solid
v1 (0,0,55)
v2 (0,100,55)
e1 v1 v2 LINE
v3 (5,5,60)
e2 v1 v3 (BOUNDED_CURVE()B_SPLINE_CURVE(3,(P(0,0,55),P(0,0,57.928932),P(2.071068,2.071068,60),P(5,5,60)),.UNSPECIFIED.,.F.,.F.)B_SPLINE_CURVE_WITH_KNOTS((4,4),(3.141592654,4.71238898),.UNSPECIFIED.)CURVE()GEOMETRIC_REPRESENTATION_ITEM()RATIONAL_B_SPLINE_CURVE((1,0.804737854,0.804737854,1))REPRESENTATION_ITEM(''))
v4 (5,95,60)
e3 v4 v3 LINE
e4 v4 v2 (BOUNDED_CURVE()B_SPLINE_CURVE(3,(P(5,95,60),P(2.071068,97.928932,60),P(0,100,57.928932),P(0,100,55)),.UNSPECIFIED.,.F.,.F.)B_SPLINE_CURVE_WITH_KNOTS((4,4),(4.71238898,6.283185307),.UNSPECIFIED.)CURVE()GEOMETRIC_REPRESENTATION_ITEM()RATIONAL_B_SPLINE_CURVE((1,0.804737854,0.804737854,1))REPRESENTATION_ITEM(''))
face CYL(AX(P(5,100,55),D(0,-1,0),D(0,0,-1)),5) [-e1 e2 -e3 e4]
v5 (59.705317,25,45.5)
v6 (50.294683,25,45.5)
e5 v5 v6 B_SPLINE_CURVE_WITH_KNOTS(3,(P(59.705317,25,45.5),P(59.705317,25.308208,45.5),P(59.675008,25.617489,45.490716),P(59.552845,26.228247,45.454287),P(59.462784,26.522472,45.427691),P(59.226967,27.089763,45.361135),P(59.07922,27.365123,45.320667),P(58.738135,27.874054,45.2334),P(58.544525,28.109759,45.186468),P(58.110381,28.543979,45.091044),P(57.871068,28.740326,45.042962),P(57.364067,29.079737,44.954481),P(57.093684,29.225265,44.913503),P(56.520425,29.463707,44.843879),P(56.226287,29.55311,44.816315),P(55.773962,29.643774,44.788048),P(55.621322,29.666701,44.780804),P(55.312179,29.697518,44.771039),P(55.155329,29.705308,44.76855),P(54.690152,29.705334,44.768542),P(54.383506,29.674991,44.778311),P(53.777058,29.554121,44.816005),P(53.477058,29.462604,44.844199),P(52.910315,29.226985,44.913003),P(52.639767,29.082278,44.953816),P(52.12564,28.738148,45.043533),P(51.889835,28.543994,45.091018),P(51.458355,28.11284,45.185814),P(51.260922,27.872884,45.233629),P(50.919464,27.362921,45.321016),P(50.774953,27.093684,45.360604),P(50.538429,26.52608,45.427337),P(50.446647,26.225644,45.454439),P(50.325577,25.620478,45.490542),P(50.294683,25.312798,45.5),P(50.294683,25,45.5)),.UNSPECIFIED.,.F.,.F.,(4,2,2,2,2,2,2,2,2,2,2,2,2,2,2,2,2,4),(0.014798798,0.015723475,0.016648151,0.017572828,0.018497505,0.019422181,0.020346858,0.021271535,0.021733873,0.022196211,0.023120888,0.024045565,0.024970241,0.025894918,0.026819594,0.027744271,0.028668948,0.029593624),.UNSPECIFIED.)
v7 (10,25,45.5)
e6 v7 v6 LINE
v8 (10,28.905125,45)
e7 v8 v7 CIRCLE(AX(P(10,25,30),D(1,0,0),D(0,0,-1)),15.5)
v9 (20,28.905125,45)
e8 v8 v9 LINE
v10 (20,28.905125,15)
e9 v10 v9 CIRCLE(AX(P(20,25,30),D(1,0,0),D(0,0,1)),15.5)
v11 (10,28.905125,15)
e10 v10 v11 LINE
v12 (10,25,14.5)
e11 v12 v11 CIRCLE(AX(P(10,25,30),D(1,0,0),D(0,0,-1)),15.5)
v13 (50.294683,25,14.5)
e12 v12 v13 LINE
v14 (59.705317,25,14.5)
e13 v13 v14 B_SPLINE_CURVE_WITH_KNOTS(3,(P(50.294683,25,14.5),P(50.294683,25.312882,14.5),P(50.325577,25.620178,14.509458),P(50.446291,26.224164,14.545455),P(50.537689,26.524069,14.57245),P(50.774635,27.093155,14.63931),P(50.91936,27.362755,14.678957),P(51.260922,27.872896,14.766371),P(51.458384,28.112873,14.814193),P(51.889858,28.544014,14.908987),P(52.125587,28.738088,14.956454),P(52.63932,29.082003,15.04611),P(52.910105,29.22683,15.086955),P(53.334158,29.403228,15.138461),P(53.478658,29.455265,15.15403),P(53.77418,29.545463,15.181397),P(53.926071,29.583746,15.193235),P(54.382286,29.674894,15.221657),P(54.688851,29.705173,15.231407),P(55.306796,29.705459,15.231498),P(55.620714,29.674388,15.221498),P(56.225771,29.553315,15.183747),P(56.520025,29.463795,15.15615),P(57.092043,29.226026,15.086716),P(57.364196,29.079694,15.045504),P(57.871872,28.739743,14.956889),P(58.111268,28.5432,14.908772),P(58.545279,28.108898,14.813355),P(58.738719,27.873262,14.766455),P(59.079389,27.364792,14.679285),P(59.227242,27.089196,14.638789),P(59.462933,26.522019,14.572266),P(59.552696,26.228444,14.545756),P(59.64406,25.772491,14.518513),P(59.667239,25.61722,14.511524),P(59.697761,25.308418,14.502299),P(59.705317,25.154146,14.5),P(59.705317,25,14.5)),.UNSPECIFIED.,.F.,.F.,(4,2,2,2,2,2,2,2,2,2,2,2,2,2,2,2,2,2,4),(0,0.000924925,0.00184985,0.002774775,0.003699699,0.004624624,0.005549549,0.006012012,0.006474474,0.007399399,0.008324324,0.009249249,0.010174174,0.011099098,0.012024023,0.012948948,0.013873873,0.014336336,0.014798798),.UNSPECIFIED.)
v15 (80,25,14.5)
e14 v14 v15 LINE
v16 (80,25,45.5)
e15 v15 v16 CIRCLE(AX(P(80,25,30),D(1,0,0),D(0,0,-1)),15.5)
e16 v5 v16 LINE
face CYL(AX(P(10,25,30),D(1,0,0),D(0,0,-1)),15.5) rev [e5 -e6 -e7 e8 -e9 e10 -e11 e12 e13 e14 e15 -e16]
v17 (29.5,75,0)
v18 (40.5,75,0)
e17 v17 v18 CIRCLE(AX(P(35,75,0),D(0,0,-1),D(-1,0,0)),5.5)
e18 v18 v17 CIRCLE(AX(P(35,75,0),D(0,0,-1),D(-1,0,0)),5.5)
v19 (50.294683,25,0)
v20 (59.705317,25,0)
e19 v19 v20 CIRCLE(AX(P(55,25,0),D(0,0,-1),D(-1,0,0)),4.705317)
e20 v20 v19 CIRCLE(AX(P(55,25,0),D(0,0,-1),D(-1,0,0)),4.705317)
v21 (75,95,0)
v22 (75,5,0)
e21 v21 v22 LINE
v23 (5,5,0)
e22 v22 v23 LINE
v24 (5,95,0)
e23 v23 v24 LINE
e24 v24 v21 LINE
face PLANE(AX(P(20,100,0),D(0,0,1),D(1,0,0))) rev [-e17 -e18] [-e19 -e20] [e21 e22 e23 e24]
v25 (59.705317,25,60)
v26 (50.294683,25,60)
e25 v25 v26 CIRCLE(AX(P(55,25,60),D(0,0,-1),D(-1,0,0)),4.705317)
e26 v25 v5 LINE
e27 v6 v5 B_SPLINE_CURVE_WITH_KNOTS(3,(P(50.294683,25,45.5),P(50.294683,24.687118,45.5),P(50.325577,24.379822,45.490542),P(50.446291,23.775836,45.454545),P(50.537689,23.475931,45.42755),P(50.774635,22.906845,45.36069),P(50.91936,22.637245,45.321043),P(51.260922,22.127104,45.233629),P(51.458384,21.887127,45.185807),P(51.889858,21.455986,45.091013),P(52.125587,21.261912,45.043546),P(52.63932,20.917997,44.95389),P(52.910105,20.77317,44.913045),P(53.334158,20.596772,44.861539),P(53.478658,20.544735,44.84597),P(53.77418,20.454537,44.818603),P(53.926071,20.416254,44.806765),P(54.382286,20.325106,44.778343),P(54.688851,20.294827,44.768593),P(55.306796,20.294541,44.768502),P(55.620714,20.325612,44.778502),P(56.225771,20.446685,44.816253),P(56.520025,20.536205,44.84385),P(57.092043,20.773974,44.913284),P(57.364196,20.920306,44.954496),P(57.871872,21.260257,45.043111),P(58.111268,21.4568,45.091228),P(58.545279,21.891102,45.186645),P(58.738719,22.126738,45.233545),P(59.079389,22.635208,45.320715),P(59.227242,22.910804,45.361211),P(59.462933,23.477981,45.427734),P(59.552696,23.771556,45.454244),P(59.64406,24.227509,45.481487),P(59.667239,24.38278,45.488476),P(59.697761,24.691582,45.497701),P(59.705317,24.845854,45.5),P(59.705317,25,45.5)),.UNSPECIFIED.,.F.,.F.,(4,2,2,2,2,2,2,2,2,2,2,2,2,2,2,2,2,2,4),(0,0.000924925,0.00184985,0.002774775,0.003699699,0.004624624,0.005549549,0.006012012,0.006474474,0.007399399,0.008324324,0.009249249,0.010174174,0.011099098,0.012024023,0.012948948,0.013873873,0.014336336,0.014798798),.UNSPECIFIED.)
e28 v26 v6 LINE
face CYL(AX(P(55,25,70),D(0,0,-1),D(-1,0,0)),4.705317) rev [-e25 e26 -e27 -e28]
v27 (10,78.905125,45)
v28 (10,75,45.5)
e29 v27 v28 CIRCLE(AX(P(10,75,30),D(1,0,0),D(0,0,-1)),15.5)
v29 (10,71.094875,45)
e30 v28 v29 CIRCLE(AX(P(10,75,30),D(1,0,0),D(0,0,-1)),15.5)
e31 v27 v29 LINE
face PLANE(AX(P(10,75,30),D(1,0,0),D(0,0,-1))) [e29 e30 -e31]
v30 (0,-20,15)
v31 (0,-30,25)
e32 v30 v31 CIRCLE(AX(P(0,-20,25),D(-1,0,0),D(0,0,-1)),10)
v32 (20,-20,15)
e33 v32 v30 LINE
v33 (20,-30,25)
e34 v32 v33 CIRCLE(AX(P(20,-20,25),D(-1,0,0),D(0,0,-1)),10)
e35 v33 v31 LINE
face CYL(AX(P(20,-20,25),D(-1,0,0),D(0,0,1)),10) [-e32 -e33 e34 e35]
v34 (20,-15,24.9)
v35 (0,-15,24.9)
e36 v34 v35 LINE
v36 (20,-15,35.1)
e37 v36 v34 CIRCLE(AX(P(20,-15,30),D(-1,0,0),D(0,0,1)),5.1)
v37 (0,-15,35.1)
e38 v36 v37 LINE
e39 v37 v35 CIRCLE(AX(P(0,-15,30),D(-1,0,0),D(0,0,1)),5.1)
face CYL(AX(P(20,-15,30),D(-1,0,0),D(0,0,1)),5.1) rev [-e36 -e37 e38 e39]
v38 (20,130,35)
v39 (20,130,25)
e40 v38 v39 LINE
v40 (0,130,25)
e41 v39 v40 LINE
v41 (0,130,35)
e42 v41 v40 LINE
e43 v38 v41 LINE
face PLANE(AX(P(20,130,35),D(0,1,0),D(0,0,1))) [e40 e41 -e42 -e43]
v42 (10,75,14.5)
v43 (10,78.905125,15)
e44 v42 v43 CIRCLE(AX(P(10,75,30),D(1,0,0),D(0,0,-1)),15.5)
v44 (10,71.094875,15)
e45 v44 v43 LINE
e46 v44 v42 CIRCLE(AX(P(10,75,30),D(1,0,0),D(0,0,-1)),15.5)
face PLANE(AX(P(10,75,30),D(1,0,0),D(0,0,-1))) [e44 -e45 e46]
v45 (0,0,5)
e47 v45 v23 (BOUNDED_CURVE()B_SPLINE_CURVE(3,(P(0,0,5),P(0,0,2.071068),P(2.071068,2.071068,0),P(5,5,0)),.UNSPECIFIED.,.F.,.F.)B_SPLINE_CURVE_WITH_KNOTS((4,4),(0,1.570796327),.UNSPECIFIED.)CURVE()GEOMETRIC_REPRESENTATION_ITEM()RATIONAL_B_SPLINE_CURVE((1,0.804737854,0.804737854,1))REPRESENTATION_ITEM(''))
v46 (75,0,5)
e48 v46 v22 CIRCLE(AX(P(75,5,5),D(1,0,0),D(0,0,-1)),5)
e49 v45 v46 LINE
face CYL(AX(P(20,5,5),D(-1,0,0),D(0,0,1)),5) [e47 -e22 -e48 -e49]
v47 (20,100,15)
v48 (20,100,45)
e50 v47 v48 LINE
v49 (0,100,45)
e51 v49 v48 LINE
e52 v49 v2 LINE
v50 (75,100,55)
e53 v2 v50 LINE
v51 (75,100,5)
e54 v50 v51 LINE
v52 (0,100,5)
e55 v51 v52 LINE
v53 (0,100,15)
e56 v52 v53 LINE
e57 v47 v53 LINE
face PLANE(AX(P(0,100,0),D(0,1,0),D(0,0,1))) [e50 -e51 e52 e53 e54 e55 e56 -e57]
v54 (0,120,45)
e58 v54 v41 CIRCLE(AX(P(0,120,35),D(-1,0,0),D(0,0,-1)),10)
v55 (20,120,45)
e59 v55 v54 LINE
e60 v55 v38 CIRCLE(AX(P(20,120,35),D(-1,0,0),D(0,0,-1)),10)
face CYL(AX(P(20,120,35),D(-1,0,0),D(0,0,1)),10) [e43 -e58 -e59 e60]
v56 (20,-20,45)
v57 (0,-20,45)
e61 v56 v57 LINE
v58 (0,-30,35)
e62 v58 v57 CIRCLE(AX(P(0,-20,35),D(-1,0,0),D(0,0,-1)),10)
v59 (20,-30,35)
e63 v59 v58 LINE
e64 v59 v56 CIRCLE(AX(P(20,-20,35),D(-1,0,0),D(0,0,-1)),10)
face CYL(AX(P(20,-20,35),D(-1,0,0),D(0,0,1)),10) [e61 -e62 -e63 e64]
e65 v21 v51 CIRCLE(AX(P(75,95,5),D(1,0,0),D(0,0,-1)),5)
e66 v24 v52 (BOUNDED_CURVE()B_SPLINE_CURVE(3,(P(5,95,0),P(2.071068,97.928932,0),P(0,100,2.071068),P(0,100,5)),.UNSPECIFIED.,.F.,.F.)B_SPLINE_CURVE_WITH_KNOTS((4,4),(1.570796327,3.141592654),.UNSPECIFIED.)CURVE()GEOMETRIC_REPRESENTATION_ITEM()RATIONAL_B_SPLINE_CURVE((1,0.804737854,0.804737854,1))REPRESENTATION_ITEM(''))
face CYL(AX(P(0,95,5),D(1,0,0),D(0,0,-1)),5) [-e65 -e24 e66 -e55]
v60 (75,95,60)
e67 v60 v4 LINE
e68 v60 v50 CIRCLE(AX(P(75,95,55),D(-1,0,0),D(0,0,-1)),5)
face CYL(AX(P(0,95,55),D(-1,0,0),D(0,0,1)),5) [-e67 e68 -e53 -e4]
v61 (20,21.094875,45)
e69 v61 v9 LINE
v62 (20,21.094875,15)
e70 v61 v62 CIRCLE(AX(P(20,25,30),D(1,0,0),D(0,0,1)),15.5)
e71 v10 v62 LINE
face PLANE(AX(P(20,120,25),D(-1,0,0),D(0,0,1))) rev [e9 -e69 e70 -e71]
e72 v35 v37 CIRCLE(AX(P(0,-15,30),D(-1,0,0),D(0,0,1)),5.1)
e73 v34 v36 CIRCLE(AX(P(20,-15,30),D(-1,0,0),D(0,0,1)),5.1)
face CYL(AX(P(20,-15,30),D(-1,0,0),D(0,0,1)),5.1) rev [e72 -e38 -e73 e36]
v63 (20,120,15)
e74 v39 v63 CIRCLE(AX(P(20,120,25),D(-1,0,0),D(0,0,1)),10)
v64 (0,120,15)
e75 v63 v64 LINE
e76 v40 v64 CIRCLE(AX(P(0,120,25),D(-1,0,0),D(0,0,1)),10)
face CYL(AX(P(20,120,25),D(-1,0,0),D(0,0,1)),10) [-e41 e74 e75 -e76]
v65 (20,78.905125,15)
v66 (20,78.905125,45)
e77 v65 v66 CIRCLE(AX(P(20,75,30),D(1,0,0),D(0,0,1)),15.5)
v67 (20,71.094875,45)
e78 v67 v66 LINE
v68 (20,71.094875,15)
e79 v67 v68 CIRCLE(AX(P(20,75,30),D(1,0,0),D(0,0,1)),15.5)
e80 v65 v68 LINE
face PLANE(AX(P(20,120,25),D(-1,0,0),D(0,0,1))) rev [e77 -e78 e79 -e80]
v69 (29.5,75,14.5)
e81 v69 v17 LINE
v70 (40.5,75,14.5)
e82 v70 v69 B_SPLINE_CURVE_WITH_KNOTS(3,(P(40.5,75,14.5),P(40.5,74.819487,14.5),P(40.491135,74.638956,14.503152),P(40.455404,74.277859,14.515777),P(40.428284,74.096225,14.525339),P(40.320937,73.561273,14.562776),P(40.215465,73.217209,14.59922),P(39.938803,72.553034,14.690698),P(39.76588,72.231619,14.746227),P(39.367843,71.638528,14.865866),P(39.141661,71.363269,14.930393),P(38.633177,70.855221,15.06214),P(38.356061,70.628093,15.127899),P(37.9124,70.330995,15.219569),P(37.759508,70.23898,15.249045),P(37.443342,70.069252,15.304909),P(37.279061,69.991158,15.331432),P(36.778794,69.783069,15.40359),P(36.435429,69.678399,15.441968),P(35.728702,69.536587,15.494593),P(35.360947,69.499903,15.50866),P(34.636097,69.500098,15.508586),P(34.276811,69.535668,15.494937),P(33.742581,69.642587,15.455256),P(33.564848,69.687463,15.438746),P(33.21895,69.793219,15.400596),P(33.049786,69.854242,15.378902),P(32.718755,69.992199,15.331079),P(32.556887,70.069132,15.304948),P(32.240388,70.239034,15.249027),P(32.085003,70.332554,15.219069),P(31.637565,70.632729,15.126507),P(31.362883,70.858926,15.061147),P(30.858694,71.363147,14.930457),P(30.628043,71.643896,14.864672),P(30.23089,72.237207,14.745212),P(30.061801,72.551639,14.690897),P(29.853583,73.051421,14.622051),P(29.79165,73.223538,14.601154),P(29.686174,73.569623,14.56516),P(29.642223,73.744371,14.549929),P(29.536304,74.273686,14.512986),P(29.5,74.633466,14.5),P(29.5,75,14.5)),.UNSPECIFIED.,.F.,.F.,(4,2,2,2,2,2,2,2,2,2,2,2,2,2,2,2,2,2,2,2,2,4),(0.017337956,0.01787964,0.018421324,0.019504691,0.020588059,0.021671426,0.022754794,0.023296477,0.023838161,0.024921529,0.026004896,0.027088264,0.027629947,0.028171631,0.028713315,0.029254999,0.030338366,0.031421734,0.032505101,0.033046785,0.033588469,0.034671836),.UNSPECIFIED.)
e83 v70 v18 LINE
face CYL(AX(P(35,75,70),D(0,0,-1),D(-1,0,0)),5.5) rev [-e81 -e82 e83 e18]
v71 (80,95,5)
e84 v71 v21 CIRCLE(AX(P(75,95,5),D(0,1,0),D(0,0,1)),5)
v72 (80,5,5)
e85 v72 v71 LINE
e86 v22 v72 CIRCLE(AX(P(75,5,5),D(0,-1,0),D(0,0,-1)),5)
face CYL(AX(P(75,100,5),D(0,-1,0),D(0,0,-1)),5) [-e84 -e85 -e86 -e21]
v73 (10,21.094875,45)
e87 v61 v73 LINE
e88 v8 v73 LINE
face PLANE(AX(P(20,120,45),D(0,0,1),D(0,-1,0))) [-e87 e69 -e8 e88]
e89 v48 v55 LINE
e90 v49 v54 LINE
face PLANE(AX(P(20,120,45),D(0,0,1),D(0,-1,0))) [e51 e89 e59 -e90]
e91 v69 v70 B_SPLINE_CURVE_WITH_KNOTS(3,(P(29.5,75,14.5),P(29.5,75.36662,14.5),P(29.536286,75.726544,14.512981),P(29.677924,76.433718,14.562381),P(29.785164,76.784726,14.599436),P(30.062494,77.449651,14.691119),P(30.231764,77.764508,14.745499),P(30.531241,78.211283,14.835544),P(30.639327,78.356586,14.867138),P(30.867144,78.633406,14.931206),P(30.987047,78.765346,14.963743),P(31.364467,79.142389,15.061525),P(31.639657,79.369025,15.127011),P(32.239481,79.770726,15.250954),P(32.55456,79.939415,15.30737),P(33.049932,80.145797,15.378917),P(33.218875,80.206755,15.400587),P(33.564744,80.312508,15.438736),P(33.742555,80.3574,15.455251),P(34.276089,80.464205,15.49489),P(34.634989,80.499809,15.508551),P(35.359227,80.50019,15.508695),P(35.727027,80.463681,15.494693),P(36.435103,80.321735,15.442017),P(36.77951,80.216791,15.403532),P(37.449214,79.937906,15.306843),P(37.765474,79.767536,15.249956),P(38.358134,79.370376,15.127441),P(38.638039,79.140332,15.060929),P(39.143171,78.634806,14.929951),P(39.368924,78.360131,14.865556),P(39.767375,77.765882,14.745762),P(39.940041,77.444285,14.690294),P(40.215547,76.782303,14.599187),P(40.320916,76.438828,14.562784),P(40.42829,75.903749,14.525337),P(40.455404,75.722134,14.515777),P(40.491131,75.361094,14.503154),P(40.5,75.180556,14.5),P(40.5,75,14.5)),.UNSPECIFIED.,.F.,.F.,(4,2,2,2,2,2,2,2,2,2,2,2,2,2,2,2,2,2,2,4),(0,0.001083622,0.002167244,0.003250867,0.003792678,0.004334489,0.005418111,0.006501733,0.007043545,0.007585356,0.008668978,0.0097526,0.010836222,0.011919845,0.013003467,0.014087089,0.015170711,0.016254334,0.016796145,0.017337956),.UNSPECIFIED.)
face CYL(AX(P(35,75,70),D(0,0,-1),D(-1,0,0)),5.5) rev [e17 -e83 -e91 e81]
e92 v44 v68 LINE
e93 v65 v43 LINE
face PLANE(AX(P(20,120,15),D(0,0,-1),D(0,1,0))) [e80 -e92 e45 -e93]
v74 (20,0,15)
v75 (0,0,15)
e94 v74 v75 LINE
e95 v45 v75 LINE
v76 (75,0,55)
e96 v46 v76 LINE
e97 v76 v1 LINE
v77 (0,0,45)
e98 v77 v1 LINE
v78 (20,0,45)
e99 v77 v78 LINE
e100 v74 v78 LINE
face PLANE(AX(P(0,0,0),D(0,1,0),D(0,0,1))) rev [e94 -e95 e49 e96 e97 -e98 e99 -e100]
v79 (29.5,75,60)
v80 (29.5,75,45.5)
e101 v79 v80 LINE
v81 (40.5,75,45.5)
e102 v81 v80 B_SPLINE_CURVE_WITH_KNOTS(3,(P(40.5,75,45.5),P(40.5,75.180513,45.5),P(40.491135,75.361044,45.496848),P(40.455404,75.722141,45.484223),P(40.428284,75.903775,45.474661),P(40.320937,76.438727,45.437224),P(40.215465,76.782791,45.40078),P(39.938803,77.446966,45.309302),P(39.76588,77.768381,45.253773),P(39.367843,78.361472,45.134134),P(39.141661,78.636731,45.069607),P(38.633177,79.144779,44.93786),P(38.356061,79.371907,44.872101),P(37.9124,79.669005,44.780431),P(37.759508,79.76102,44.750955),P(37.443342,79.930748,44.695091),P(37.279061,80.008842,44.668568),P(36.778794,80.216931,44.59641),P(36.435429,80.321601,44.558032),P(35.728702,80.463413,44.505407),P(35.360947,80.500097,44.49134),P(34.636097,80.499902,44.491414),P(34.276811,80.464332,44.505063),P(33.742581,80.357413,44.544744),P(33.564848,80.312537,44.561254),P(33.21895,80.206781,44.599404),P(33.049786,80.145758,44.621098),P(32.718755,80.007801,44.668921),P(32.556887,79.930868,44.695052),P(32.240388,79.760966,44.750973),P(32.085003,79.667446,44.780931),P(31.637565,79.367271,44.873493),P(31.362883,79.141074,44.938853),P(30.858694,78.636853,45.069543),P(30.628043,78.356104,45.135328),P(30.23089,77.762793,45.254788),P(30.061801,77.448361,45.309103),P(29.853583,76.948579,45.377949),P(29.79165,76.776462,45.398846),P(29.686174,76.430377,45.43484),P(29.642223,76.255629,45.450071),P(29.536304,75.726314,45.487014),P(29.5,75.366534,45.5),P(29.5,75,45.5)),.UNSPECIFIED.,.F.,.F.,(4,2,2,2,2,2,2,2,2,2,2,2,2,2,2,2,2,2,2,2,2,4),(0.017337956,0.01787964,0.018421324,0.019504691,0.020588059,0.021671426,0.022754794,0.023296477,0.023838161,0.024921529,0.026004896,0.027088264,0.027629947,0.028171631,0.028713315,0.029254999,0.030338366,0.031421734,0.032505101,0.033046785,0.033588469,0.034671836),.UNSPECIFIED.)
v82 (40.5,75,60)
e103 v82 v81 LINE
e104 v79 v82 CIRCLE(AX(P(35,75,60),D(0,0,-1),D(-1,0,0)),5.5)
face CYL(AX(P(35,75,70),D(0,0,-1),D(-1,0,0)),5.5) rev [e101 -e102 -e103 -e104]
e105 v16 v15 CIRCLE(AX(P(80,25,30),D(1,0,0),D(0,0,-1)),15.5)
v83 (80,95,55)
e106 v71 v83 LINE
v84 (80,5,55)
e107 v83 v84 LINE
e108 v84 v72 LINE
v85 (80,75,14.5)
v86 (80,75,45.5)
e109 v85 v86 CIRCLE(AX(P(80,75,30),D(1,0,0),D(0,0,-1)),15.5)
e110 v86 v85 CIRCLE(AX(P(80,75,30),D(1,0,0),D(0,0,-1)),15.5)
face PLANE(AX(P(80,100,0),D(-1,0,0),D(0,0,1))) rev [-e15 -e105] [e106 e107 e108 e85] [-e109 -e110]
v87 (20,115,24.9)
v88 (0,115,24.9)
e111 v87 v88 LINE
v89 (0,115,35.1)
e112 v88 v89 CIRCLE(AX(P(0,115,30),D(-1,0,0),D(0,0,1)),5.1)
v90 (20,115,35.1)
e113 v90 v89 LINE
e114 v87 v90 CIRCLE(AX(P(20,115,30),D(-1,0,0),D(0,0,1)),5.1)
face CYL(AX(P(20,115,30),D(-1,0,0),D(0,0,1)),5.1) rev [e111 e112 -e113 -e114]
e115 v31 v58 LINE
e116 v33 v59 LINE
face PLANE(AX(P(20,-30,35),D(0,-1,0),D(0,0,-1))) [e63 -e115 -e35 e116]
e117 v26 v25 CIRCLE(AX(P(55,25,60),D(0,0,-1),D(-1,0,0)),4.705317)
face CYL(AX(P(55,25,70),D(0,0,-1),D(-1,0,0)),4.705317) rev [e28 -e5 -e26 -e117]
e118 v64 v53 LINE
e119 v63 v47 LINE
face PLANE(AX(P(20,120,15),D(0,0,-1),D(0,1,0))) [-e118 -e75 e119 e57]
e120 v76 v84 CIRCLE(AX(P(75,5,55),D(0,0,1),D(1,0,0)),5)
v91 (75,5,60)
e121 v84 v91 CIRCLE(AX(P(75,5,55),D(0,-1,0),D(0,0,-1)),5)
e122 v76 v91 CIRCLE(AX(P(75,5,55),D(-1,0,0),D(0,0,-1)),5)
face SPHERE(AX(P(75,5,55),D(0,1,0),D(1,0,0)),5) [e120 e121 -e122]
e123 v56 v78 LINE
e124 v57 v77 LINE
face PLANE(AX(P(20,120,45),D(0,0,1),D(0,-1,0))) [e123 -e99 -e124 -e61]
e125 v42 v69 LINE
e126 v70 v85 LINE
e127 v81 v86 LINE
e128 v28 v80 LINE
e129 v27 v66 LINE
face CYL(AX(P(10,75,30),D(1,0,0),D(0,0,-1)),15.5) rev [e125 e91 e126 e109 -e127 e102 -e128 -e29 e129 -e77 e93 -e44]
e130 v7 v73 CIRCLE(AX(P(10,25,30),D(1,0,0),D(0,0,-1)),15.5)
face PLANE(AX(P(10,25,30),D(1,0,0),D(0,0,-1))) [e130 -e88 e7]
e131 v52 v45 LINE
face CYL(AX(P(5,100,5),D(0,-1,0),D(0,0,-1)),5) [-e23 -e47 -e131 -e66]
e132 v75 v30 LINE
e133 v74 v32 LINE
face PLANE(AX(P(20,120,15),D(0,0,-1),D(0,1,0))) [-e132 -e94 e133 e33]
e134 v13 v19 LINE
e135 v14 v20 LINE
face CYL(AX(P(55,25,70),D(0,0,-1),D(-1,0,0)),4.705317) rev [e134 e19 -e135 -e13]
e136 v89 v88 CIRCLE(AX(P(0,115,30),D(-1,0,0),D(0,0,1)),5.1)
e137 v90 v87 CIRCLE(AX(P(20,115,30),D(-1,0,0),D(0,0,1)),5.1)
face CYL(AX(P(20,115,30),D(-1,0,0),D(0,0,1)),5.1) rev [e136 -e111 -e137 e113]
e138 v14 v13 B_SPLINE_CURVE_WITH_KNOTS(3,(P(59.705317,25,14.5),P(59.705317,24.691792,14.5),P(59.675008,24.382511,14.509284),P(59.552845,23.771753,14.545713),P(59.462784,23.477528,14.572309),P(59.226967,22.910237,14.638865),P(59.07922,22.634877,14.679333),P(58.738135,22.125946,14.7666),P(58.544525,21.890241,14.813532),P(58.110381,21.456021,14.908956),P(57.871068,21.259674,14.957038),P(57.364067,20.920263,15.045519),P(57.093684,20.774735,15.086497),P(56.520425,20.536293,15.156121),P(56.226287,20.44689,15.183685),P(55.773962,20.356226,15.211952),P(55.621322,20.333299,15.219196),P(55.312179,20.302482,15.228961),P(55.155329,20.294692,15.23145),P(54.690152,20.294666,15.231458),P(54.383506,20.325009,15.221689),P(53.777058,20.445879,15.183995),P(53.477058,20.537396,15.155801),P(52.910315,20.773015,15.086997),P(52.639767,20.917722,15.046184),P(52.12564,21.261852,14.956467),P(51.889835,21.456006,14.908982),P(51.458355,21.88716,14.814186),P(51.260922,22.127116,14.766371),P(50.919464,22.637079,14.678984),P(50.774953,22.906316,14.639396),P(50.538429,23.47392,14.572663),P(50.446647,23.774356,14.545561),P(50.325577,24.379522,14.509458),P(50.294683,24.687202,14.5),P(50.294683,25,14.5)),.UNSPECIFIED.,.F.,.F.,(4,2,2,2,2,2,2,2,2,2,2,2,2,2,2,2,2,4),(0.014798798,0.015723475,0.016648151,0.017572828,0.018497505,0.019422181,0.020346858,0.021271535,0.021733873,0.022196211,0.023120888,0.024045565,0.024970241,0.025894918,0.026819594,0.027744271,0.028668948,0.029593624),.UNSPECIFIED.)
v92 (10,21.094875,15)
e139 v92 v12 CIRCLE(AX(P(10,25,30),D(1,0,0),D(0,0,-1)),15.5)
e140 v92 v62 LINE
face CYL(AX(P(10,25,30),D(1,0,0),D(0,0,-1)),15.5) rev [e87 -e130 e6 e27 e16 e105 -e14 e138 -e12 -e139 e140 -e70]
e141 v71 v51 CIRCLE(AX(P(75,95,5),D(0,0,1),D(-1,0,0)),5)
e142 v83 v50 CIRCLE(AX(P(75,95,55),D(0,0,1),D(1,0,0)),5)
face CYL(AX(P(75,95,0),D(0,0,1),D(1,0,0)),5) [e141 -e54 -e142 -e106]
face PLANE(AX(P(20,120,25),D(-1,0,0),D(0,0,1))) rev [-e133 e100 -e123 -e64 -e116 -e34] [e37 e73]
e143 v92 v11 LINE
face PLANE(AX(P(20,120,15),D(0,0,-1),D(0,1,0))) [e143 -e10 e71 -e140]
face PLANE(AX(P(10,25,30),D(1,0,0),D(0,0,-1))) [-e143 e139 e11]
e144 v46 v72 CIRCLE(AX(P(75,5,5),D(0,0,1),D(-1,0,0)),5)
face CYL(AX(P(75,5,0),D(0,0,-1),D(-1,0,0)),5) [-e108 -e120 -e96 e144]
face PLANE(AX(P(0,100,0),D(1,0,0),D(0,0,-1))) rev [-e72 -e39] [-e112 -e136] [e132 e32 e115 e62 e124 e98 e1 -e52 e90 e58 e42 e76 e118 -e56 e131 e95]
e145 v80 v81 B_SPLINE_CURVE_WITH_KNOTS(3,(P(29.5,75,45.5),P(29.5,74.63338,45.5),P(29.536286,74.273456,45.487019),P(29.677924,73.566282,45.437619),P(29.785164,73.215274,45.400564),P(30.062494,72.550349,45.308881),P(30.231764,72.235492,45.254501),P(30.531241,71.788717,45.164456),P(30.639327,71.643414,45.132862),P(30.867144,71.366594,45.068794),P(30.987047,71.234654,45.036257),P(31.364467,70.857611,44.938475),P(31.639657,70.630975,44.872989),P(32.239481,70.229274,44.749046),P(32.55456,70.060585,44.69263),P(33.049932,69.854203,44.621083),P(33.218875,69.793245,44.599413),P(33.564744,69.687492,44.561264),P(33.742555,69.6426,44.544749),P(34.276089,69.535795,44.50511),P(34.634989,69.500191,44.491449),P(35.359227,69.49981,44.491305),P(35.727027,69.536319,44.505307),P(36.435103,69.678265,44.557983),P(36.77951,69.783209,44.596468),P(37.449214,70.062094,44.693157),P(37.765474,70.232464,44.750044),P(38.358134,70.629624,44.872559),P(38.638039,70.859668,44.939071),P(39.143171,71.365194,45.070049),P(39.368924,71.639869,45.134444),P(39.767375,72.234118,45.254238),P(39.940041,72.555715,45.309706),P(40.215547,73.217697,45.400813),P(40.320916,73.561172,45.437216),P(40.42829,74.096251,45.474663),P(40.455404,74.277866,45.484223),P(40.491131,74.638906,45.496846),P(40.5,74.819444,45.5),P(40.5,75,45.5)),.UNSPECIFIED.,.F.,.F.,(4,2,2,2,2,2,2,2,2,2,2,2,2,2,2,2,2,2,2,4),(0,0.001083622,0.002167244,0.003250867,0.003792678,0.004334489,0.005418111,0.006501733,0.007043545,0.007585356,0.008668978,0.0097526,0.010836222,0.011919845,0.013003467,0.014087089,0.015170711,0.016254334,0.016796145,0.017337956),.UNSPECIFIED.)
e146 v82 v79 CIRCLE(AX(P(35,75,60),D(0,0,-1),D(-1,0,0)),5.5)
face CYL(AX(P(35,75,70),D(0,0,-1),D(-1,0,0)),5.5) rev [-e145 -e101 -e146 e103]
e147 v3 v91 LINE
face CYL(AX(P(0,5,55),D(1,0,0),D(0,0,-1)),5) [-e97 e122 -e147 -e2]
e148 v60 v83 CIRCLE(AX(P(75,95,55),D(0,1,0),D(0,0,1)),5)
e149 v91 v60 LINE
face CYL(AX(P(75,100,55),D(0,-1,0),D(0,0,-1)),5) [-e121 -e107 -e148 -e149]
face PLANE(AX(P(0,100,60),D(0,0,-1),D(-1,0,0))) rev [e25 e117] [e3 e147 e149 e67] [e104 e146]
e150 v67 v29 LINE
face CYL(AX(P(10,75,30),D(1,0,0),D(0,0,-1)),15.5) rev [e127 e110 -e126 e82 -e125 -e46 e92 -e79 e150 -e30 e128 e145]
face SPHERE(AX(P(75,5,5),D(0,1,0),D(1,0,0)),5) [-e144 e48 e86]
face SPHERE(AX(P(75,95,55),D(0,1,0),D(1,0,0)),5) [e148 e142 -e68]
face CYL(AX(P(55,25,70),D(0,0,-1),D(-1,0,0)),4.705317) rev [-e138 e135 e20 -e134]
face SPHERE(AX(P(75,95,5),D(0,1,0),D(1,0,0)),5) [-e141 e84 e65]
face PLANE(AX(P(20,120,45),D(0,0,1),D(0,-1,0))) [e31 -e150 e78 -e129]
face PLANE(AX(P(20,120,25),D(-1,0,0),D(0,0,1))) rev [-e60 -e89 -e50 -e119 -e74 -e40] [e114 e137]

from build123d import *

# Parameters (mm, degrees)
BOSS_EXTRUDE1_DEPTH = 100
SKETCH2_R           = 15.5
CUT_EXTRUDE1_DEPTH  = 70
SKETCH3_R           = 5.1
CUT_EXTRUDE2_DEPTH  = 70
SKETCH4_R           = 5.5
SKETCH4_R_2         = 4.705316684
CUT_EXTRUDE3_DEPTH  = 70
SKETCH5_R           = 5.1
BOSS_EXTRUDE2_DEPTH = 20
SKETCH6_W           = 20
SKETCH6_H           = 100
CUT_EXTRUDE4_DEPTH  = 20
FILLET1_R           = 5


with BuildPart() as part:
    # Sketch1 → Boss-Extrude1 (new body)
    with BuildSketch(Plane(origin=(0, 0, 0), x_dir=(1, 0, 0), z_dir=(0, 1, 0))):
        Polygon((0, 20), (20, 20), (20, 0), (80, 0), (80, -60), (0, -60), (0, 0), align=None)
    extrude(amount=BOSS_EXTRUDE1_DEPTH)

    # Sketch2 → Cut-Extrude1 (cut)
    with BuildSketch(Plane(origin=(80, 0, 0), x_dir=(0, 0, -1), z_dir=(1, 0, 0))):
        with Locations((-30, 75)):
            Circle(SKETCH2_R)
        with Locations((-30, 25)):
            Circle(SKETCH2_R)
    extrude(amount=-CUT_EXTRUDE1_DEPTH, mode=Mode.SUBTRACT)

    # Sketch3 → Cut-Extrude2 (cut)
    with BuildSketch(Plane(origin=(20, 0, 0), x_dir=(0, 0, -1), z_dir=(1, 0, 0))):
        with Locations((10, 87.5)):
            Circle(SKETCH3_R)
        with Locations((10, 12.5)):
            Circle(SKETCH3_R)
        with Locations((10, 50)):
            Circle(SKETCH3_R)
    extrude(amount=-CUT_EXTRUDE2_DEPTH, mode=Mode.SUBTRACT)

    # Sketch4 → Cut-Extrude3 (cut)
    with BuildSketch(Plane(origin=(0, 0, 0), x_dir=(-1, 0, 0), z_dir=(0, 0, -1))):
        with Locations((-35, 75)):
            Circle(SKETCH4_R)
        with Locations((-55, 25)):
            Circle(SKETCH4_R_2)
    extrude(amount=-CUT_EXTRUDE3_DEPTH, mode=Mode.SUBTRACT)

    # Sketch5 → Boss-Extrude2 (add)
    with BuildSketch(Plane.ZY):
        with BuildLine():
            Line((35, 130), (25, 130))
            ThreePointArc((25, 130), (17.928932188, 127.071067812), (15, 120))
            Line((15, 120), (15, -20))
            ThreePointArc((15, -20), (17.928932188, -27.071067812), (25, -30))
            Line((25, -30), (35, -30))
            ThreePointArc((35, -30), (42.071067812, -27.071067812), (45, -20))
            Line((45, -20), (45, 120))
            ThreePointArc((45, 120), (42.071067812, 127.071067812), (35, 130))
        make_face()
        with Locations((30, -15)):
            Circle(SKETCH5_R, mode=Mode.SUBTRACT)
        with Locations((30, 115)):
            Circle(SKETCH5_R, mode=Mode.SUBTRACT)
    extrude(amount=-BOSS_EXTRUDE2_DEPTH)

    # Sketch6 → Cut-Extrude4 (cut)
    with BuildSketch(Plane(origin=(20, 0, 0), x_dir=(0, 0, -1), z_dir=(1, 0, 0))):
        with Locations((10, 50)):
            Rectangle(SKETCH6_W, SKETCH6_H)
    extrude(amount=-CUT_EXTRUDE4_DEPTH, mode=Mode.SUBTRACT)

    # Fillet1
    fillet1_edges = [part.edges().sort_by_distance(p)[0] for p in [
        (80, 100, 30),
        (80, 50, 0),
        (80, 50, 60),
        (0, 50, 60),
        (40, 100, 0),
        (0, 50, 0),
        (40, 100, 60),
        (40, 0, 0),
        (80, 0, 30),
        (40, 0, 60),
    ]]
    fillet(fillet1_edges, radius=FILLET1_R)


solid = part.part
